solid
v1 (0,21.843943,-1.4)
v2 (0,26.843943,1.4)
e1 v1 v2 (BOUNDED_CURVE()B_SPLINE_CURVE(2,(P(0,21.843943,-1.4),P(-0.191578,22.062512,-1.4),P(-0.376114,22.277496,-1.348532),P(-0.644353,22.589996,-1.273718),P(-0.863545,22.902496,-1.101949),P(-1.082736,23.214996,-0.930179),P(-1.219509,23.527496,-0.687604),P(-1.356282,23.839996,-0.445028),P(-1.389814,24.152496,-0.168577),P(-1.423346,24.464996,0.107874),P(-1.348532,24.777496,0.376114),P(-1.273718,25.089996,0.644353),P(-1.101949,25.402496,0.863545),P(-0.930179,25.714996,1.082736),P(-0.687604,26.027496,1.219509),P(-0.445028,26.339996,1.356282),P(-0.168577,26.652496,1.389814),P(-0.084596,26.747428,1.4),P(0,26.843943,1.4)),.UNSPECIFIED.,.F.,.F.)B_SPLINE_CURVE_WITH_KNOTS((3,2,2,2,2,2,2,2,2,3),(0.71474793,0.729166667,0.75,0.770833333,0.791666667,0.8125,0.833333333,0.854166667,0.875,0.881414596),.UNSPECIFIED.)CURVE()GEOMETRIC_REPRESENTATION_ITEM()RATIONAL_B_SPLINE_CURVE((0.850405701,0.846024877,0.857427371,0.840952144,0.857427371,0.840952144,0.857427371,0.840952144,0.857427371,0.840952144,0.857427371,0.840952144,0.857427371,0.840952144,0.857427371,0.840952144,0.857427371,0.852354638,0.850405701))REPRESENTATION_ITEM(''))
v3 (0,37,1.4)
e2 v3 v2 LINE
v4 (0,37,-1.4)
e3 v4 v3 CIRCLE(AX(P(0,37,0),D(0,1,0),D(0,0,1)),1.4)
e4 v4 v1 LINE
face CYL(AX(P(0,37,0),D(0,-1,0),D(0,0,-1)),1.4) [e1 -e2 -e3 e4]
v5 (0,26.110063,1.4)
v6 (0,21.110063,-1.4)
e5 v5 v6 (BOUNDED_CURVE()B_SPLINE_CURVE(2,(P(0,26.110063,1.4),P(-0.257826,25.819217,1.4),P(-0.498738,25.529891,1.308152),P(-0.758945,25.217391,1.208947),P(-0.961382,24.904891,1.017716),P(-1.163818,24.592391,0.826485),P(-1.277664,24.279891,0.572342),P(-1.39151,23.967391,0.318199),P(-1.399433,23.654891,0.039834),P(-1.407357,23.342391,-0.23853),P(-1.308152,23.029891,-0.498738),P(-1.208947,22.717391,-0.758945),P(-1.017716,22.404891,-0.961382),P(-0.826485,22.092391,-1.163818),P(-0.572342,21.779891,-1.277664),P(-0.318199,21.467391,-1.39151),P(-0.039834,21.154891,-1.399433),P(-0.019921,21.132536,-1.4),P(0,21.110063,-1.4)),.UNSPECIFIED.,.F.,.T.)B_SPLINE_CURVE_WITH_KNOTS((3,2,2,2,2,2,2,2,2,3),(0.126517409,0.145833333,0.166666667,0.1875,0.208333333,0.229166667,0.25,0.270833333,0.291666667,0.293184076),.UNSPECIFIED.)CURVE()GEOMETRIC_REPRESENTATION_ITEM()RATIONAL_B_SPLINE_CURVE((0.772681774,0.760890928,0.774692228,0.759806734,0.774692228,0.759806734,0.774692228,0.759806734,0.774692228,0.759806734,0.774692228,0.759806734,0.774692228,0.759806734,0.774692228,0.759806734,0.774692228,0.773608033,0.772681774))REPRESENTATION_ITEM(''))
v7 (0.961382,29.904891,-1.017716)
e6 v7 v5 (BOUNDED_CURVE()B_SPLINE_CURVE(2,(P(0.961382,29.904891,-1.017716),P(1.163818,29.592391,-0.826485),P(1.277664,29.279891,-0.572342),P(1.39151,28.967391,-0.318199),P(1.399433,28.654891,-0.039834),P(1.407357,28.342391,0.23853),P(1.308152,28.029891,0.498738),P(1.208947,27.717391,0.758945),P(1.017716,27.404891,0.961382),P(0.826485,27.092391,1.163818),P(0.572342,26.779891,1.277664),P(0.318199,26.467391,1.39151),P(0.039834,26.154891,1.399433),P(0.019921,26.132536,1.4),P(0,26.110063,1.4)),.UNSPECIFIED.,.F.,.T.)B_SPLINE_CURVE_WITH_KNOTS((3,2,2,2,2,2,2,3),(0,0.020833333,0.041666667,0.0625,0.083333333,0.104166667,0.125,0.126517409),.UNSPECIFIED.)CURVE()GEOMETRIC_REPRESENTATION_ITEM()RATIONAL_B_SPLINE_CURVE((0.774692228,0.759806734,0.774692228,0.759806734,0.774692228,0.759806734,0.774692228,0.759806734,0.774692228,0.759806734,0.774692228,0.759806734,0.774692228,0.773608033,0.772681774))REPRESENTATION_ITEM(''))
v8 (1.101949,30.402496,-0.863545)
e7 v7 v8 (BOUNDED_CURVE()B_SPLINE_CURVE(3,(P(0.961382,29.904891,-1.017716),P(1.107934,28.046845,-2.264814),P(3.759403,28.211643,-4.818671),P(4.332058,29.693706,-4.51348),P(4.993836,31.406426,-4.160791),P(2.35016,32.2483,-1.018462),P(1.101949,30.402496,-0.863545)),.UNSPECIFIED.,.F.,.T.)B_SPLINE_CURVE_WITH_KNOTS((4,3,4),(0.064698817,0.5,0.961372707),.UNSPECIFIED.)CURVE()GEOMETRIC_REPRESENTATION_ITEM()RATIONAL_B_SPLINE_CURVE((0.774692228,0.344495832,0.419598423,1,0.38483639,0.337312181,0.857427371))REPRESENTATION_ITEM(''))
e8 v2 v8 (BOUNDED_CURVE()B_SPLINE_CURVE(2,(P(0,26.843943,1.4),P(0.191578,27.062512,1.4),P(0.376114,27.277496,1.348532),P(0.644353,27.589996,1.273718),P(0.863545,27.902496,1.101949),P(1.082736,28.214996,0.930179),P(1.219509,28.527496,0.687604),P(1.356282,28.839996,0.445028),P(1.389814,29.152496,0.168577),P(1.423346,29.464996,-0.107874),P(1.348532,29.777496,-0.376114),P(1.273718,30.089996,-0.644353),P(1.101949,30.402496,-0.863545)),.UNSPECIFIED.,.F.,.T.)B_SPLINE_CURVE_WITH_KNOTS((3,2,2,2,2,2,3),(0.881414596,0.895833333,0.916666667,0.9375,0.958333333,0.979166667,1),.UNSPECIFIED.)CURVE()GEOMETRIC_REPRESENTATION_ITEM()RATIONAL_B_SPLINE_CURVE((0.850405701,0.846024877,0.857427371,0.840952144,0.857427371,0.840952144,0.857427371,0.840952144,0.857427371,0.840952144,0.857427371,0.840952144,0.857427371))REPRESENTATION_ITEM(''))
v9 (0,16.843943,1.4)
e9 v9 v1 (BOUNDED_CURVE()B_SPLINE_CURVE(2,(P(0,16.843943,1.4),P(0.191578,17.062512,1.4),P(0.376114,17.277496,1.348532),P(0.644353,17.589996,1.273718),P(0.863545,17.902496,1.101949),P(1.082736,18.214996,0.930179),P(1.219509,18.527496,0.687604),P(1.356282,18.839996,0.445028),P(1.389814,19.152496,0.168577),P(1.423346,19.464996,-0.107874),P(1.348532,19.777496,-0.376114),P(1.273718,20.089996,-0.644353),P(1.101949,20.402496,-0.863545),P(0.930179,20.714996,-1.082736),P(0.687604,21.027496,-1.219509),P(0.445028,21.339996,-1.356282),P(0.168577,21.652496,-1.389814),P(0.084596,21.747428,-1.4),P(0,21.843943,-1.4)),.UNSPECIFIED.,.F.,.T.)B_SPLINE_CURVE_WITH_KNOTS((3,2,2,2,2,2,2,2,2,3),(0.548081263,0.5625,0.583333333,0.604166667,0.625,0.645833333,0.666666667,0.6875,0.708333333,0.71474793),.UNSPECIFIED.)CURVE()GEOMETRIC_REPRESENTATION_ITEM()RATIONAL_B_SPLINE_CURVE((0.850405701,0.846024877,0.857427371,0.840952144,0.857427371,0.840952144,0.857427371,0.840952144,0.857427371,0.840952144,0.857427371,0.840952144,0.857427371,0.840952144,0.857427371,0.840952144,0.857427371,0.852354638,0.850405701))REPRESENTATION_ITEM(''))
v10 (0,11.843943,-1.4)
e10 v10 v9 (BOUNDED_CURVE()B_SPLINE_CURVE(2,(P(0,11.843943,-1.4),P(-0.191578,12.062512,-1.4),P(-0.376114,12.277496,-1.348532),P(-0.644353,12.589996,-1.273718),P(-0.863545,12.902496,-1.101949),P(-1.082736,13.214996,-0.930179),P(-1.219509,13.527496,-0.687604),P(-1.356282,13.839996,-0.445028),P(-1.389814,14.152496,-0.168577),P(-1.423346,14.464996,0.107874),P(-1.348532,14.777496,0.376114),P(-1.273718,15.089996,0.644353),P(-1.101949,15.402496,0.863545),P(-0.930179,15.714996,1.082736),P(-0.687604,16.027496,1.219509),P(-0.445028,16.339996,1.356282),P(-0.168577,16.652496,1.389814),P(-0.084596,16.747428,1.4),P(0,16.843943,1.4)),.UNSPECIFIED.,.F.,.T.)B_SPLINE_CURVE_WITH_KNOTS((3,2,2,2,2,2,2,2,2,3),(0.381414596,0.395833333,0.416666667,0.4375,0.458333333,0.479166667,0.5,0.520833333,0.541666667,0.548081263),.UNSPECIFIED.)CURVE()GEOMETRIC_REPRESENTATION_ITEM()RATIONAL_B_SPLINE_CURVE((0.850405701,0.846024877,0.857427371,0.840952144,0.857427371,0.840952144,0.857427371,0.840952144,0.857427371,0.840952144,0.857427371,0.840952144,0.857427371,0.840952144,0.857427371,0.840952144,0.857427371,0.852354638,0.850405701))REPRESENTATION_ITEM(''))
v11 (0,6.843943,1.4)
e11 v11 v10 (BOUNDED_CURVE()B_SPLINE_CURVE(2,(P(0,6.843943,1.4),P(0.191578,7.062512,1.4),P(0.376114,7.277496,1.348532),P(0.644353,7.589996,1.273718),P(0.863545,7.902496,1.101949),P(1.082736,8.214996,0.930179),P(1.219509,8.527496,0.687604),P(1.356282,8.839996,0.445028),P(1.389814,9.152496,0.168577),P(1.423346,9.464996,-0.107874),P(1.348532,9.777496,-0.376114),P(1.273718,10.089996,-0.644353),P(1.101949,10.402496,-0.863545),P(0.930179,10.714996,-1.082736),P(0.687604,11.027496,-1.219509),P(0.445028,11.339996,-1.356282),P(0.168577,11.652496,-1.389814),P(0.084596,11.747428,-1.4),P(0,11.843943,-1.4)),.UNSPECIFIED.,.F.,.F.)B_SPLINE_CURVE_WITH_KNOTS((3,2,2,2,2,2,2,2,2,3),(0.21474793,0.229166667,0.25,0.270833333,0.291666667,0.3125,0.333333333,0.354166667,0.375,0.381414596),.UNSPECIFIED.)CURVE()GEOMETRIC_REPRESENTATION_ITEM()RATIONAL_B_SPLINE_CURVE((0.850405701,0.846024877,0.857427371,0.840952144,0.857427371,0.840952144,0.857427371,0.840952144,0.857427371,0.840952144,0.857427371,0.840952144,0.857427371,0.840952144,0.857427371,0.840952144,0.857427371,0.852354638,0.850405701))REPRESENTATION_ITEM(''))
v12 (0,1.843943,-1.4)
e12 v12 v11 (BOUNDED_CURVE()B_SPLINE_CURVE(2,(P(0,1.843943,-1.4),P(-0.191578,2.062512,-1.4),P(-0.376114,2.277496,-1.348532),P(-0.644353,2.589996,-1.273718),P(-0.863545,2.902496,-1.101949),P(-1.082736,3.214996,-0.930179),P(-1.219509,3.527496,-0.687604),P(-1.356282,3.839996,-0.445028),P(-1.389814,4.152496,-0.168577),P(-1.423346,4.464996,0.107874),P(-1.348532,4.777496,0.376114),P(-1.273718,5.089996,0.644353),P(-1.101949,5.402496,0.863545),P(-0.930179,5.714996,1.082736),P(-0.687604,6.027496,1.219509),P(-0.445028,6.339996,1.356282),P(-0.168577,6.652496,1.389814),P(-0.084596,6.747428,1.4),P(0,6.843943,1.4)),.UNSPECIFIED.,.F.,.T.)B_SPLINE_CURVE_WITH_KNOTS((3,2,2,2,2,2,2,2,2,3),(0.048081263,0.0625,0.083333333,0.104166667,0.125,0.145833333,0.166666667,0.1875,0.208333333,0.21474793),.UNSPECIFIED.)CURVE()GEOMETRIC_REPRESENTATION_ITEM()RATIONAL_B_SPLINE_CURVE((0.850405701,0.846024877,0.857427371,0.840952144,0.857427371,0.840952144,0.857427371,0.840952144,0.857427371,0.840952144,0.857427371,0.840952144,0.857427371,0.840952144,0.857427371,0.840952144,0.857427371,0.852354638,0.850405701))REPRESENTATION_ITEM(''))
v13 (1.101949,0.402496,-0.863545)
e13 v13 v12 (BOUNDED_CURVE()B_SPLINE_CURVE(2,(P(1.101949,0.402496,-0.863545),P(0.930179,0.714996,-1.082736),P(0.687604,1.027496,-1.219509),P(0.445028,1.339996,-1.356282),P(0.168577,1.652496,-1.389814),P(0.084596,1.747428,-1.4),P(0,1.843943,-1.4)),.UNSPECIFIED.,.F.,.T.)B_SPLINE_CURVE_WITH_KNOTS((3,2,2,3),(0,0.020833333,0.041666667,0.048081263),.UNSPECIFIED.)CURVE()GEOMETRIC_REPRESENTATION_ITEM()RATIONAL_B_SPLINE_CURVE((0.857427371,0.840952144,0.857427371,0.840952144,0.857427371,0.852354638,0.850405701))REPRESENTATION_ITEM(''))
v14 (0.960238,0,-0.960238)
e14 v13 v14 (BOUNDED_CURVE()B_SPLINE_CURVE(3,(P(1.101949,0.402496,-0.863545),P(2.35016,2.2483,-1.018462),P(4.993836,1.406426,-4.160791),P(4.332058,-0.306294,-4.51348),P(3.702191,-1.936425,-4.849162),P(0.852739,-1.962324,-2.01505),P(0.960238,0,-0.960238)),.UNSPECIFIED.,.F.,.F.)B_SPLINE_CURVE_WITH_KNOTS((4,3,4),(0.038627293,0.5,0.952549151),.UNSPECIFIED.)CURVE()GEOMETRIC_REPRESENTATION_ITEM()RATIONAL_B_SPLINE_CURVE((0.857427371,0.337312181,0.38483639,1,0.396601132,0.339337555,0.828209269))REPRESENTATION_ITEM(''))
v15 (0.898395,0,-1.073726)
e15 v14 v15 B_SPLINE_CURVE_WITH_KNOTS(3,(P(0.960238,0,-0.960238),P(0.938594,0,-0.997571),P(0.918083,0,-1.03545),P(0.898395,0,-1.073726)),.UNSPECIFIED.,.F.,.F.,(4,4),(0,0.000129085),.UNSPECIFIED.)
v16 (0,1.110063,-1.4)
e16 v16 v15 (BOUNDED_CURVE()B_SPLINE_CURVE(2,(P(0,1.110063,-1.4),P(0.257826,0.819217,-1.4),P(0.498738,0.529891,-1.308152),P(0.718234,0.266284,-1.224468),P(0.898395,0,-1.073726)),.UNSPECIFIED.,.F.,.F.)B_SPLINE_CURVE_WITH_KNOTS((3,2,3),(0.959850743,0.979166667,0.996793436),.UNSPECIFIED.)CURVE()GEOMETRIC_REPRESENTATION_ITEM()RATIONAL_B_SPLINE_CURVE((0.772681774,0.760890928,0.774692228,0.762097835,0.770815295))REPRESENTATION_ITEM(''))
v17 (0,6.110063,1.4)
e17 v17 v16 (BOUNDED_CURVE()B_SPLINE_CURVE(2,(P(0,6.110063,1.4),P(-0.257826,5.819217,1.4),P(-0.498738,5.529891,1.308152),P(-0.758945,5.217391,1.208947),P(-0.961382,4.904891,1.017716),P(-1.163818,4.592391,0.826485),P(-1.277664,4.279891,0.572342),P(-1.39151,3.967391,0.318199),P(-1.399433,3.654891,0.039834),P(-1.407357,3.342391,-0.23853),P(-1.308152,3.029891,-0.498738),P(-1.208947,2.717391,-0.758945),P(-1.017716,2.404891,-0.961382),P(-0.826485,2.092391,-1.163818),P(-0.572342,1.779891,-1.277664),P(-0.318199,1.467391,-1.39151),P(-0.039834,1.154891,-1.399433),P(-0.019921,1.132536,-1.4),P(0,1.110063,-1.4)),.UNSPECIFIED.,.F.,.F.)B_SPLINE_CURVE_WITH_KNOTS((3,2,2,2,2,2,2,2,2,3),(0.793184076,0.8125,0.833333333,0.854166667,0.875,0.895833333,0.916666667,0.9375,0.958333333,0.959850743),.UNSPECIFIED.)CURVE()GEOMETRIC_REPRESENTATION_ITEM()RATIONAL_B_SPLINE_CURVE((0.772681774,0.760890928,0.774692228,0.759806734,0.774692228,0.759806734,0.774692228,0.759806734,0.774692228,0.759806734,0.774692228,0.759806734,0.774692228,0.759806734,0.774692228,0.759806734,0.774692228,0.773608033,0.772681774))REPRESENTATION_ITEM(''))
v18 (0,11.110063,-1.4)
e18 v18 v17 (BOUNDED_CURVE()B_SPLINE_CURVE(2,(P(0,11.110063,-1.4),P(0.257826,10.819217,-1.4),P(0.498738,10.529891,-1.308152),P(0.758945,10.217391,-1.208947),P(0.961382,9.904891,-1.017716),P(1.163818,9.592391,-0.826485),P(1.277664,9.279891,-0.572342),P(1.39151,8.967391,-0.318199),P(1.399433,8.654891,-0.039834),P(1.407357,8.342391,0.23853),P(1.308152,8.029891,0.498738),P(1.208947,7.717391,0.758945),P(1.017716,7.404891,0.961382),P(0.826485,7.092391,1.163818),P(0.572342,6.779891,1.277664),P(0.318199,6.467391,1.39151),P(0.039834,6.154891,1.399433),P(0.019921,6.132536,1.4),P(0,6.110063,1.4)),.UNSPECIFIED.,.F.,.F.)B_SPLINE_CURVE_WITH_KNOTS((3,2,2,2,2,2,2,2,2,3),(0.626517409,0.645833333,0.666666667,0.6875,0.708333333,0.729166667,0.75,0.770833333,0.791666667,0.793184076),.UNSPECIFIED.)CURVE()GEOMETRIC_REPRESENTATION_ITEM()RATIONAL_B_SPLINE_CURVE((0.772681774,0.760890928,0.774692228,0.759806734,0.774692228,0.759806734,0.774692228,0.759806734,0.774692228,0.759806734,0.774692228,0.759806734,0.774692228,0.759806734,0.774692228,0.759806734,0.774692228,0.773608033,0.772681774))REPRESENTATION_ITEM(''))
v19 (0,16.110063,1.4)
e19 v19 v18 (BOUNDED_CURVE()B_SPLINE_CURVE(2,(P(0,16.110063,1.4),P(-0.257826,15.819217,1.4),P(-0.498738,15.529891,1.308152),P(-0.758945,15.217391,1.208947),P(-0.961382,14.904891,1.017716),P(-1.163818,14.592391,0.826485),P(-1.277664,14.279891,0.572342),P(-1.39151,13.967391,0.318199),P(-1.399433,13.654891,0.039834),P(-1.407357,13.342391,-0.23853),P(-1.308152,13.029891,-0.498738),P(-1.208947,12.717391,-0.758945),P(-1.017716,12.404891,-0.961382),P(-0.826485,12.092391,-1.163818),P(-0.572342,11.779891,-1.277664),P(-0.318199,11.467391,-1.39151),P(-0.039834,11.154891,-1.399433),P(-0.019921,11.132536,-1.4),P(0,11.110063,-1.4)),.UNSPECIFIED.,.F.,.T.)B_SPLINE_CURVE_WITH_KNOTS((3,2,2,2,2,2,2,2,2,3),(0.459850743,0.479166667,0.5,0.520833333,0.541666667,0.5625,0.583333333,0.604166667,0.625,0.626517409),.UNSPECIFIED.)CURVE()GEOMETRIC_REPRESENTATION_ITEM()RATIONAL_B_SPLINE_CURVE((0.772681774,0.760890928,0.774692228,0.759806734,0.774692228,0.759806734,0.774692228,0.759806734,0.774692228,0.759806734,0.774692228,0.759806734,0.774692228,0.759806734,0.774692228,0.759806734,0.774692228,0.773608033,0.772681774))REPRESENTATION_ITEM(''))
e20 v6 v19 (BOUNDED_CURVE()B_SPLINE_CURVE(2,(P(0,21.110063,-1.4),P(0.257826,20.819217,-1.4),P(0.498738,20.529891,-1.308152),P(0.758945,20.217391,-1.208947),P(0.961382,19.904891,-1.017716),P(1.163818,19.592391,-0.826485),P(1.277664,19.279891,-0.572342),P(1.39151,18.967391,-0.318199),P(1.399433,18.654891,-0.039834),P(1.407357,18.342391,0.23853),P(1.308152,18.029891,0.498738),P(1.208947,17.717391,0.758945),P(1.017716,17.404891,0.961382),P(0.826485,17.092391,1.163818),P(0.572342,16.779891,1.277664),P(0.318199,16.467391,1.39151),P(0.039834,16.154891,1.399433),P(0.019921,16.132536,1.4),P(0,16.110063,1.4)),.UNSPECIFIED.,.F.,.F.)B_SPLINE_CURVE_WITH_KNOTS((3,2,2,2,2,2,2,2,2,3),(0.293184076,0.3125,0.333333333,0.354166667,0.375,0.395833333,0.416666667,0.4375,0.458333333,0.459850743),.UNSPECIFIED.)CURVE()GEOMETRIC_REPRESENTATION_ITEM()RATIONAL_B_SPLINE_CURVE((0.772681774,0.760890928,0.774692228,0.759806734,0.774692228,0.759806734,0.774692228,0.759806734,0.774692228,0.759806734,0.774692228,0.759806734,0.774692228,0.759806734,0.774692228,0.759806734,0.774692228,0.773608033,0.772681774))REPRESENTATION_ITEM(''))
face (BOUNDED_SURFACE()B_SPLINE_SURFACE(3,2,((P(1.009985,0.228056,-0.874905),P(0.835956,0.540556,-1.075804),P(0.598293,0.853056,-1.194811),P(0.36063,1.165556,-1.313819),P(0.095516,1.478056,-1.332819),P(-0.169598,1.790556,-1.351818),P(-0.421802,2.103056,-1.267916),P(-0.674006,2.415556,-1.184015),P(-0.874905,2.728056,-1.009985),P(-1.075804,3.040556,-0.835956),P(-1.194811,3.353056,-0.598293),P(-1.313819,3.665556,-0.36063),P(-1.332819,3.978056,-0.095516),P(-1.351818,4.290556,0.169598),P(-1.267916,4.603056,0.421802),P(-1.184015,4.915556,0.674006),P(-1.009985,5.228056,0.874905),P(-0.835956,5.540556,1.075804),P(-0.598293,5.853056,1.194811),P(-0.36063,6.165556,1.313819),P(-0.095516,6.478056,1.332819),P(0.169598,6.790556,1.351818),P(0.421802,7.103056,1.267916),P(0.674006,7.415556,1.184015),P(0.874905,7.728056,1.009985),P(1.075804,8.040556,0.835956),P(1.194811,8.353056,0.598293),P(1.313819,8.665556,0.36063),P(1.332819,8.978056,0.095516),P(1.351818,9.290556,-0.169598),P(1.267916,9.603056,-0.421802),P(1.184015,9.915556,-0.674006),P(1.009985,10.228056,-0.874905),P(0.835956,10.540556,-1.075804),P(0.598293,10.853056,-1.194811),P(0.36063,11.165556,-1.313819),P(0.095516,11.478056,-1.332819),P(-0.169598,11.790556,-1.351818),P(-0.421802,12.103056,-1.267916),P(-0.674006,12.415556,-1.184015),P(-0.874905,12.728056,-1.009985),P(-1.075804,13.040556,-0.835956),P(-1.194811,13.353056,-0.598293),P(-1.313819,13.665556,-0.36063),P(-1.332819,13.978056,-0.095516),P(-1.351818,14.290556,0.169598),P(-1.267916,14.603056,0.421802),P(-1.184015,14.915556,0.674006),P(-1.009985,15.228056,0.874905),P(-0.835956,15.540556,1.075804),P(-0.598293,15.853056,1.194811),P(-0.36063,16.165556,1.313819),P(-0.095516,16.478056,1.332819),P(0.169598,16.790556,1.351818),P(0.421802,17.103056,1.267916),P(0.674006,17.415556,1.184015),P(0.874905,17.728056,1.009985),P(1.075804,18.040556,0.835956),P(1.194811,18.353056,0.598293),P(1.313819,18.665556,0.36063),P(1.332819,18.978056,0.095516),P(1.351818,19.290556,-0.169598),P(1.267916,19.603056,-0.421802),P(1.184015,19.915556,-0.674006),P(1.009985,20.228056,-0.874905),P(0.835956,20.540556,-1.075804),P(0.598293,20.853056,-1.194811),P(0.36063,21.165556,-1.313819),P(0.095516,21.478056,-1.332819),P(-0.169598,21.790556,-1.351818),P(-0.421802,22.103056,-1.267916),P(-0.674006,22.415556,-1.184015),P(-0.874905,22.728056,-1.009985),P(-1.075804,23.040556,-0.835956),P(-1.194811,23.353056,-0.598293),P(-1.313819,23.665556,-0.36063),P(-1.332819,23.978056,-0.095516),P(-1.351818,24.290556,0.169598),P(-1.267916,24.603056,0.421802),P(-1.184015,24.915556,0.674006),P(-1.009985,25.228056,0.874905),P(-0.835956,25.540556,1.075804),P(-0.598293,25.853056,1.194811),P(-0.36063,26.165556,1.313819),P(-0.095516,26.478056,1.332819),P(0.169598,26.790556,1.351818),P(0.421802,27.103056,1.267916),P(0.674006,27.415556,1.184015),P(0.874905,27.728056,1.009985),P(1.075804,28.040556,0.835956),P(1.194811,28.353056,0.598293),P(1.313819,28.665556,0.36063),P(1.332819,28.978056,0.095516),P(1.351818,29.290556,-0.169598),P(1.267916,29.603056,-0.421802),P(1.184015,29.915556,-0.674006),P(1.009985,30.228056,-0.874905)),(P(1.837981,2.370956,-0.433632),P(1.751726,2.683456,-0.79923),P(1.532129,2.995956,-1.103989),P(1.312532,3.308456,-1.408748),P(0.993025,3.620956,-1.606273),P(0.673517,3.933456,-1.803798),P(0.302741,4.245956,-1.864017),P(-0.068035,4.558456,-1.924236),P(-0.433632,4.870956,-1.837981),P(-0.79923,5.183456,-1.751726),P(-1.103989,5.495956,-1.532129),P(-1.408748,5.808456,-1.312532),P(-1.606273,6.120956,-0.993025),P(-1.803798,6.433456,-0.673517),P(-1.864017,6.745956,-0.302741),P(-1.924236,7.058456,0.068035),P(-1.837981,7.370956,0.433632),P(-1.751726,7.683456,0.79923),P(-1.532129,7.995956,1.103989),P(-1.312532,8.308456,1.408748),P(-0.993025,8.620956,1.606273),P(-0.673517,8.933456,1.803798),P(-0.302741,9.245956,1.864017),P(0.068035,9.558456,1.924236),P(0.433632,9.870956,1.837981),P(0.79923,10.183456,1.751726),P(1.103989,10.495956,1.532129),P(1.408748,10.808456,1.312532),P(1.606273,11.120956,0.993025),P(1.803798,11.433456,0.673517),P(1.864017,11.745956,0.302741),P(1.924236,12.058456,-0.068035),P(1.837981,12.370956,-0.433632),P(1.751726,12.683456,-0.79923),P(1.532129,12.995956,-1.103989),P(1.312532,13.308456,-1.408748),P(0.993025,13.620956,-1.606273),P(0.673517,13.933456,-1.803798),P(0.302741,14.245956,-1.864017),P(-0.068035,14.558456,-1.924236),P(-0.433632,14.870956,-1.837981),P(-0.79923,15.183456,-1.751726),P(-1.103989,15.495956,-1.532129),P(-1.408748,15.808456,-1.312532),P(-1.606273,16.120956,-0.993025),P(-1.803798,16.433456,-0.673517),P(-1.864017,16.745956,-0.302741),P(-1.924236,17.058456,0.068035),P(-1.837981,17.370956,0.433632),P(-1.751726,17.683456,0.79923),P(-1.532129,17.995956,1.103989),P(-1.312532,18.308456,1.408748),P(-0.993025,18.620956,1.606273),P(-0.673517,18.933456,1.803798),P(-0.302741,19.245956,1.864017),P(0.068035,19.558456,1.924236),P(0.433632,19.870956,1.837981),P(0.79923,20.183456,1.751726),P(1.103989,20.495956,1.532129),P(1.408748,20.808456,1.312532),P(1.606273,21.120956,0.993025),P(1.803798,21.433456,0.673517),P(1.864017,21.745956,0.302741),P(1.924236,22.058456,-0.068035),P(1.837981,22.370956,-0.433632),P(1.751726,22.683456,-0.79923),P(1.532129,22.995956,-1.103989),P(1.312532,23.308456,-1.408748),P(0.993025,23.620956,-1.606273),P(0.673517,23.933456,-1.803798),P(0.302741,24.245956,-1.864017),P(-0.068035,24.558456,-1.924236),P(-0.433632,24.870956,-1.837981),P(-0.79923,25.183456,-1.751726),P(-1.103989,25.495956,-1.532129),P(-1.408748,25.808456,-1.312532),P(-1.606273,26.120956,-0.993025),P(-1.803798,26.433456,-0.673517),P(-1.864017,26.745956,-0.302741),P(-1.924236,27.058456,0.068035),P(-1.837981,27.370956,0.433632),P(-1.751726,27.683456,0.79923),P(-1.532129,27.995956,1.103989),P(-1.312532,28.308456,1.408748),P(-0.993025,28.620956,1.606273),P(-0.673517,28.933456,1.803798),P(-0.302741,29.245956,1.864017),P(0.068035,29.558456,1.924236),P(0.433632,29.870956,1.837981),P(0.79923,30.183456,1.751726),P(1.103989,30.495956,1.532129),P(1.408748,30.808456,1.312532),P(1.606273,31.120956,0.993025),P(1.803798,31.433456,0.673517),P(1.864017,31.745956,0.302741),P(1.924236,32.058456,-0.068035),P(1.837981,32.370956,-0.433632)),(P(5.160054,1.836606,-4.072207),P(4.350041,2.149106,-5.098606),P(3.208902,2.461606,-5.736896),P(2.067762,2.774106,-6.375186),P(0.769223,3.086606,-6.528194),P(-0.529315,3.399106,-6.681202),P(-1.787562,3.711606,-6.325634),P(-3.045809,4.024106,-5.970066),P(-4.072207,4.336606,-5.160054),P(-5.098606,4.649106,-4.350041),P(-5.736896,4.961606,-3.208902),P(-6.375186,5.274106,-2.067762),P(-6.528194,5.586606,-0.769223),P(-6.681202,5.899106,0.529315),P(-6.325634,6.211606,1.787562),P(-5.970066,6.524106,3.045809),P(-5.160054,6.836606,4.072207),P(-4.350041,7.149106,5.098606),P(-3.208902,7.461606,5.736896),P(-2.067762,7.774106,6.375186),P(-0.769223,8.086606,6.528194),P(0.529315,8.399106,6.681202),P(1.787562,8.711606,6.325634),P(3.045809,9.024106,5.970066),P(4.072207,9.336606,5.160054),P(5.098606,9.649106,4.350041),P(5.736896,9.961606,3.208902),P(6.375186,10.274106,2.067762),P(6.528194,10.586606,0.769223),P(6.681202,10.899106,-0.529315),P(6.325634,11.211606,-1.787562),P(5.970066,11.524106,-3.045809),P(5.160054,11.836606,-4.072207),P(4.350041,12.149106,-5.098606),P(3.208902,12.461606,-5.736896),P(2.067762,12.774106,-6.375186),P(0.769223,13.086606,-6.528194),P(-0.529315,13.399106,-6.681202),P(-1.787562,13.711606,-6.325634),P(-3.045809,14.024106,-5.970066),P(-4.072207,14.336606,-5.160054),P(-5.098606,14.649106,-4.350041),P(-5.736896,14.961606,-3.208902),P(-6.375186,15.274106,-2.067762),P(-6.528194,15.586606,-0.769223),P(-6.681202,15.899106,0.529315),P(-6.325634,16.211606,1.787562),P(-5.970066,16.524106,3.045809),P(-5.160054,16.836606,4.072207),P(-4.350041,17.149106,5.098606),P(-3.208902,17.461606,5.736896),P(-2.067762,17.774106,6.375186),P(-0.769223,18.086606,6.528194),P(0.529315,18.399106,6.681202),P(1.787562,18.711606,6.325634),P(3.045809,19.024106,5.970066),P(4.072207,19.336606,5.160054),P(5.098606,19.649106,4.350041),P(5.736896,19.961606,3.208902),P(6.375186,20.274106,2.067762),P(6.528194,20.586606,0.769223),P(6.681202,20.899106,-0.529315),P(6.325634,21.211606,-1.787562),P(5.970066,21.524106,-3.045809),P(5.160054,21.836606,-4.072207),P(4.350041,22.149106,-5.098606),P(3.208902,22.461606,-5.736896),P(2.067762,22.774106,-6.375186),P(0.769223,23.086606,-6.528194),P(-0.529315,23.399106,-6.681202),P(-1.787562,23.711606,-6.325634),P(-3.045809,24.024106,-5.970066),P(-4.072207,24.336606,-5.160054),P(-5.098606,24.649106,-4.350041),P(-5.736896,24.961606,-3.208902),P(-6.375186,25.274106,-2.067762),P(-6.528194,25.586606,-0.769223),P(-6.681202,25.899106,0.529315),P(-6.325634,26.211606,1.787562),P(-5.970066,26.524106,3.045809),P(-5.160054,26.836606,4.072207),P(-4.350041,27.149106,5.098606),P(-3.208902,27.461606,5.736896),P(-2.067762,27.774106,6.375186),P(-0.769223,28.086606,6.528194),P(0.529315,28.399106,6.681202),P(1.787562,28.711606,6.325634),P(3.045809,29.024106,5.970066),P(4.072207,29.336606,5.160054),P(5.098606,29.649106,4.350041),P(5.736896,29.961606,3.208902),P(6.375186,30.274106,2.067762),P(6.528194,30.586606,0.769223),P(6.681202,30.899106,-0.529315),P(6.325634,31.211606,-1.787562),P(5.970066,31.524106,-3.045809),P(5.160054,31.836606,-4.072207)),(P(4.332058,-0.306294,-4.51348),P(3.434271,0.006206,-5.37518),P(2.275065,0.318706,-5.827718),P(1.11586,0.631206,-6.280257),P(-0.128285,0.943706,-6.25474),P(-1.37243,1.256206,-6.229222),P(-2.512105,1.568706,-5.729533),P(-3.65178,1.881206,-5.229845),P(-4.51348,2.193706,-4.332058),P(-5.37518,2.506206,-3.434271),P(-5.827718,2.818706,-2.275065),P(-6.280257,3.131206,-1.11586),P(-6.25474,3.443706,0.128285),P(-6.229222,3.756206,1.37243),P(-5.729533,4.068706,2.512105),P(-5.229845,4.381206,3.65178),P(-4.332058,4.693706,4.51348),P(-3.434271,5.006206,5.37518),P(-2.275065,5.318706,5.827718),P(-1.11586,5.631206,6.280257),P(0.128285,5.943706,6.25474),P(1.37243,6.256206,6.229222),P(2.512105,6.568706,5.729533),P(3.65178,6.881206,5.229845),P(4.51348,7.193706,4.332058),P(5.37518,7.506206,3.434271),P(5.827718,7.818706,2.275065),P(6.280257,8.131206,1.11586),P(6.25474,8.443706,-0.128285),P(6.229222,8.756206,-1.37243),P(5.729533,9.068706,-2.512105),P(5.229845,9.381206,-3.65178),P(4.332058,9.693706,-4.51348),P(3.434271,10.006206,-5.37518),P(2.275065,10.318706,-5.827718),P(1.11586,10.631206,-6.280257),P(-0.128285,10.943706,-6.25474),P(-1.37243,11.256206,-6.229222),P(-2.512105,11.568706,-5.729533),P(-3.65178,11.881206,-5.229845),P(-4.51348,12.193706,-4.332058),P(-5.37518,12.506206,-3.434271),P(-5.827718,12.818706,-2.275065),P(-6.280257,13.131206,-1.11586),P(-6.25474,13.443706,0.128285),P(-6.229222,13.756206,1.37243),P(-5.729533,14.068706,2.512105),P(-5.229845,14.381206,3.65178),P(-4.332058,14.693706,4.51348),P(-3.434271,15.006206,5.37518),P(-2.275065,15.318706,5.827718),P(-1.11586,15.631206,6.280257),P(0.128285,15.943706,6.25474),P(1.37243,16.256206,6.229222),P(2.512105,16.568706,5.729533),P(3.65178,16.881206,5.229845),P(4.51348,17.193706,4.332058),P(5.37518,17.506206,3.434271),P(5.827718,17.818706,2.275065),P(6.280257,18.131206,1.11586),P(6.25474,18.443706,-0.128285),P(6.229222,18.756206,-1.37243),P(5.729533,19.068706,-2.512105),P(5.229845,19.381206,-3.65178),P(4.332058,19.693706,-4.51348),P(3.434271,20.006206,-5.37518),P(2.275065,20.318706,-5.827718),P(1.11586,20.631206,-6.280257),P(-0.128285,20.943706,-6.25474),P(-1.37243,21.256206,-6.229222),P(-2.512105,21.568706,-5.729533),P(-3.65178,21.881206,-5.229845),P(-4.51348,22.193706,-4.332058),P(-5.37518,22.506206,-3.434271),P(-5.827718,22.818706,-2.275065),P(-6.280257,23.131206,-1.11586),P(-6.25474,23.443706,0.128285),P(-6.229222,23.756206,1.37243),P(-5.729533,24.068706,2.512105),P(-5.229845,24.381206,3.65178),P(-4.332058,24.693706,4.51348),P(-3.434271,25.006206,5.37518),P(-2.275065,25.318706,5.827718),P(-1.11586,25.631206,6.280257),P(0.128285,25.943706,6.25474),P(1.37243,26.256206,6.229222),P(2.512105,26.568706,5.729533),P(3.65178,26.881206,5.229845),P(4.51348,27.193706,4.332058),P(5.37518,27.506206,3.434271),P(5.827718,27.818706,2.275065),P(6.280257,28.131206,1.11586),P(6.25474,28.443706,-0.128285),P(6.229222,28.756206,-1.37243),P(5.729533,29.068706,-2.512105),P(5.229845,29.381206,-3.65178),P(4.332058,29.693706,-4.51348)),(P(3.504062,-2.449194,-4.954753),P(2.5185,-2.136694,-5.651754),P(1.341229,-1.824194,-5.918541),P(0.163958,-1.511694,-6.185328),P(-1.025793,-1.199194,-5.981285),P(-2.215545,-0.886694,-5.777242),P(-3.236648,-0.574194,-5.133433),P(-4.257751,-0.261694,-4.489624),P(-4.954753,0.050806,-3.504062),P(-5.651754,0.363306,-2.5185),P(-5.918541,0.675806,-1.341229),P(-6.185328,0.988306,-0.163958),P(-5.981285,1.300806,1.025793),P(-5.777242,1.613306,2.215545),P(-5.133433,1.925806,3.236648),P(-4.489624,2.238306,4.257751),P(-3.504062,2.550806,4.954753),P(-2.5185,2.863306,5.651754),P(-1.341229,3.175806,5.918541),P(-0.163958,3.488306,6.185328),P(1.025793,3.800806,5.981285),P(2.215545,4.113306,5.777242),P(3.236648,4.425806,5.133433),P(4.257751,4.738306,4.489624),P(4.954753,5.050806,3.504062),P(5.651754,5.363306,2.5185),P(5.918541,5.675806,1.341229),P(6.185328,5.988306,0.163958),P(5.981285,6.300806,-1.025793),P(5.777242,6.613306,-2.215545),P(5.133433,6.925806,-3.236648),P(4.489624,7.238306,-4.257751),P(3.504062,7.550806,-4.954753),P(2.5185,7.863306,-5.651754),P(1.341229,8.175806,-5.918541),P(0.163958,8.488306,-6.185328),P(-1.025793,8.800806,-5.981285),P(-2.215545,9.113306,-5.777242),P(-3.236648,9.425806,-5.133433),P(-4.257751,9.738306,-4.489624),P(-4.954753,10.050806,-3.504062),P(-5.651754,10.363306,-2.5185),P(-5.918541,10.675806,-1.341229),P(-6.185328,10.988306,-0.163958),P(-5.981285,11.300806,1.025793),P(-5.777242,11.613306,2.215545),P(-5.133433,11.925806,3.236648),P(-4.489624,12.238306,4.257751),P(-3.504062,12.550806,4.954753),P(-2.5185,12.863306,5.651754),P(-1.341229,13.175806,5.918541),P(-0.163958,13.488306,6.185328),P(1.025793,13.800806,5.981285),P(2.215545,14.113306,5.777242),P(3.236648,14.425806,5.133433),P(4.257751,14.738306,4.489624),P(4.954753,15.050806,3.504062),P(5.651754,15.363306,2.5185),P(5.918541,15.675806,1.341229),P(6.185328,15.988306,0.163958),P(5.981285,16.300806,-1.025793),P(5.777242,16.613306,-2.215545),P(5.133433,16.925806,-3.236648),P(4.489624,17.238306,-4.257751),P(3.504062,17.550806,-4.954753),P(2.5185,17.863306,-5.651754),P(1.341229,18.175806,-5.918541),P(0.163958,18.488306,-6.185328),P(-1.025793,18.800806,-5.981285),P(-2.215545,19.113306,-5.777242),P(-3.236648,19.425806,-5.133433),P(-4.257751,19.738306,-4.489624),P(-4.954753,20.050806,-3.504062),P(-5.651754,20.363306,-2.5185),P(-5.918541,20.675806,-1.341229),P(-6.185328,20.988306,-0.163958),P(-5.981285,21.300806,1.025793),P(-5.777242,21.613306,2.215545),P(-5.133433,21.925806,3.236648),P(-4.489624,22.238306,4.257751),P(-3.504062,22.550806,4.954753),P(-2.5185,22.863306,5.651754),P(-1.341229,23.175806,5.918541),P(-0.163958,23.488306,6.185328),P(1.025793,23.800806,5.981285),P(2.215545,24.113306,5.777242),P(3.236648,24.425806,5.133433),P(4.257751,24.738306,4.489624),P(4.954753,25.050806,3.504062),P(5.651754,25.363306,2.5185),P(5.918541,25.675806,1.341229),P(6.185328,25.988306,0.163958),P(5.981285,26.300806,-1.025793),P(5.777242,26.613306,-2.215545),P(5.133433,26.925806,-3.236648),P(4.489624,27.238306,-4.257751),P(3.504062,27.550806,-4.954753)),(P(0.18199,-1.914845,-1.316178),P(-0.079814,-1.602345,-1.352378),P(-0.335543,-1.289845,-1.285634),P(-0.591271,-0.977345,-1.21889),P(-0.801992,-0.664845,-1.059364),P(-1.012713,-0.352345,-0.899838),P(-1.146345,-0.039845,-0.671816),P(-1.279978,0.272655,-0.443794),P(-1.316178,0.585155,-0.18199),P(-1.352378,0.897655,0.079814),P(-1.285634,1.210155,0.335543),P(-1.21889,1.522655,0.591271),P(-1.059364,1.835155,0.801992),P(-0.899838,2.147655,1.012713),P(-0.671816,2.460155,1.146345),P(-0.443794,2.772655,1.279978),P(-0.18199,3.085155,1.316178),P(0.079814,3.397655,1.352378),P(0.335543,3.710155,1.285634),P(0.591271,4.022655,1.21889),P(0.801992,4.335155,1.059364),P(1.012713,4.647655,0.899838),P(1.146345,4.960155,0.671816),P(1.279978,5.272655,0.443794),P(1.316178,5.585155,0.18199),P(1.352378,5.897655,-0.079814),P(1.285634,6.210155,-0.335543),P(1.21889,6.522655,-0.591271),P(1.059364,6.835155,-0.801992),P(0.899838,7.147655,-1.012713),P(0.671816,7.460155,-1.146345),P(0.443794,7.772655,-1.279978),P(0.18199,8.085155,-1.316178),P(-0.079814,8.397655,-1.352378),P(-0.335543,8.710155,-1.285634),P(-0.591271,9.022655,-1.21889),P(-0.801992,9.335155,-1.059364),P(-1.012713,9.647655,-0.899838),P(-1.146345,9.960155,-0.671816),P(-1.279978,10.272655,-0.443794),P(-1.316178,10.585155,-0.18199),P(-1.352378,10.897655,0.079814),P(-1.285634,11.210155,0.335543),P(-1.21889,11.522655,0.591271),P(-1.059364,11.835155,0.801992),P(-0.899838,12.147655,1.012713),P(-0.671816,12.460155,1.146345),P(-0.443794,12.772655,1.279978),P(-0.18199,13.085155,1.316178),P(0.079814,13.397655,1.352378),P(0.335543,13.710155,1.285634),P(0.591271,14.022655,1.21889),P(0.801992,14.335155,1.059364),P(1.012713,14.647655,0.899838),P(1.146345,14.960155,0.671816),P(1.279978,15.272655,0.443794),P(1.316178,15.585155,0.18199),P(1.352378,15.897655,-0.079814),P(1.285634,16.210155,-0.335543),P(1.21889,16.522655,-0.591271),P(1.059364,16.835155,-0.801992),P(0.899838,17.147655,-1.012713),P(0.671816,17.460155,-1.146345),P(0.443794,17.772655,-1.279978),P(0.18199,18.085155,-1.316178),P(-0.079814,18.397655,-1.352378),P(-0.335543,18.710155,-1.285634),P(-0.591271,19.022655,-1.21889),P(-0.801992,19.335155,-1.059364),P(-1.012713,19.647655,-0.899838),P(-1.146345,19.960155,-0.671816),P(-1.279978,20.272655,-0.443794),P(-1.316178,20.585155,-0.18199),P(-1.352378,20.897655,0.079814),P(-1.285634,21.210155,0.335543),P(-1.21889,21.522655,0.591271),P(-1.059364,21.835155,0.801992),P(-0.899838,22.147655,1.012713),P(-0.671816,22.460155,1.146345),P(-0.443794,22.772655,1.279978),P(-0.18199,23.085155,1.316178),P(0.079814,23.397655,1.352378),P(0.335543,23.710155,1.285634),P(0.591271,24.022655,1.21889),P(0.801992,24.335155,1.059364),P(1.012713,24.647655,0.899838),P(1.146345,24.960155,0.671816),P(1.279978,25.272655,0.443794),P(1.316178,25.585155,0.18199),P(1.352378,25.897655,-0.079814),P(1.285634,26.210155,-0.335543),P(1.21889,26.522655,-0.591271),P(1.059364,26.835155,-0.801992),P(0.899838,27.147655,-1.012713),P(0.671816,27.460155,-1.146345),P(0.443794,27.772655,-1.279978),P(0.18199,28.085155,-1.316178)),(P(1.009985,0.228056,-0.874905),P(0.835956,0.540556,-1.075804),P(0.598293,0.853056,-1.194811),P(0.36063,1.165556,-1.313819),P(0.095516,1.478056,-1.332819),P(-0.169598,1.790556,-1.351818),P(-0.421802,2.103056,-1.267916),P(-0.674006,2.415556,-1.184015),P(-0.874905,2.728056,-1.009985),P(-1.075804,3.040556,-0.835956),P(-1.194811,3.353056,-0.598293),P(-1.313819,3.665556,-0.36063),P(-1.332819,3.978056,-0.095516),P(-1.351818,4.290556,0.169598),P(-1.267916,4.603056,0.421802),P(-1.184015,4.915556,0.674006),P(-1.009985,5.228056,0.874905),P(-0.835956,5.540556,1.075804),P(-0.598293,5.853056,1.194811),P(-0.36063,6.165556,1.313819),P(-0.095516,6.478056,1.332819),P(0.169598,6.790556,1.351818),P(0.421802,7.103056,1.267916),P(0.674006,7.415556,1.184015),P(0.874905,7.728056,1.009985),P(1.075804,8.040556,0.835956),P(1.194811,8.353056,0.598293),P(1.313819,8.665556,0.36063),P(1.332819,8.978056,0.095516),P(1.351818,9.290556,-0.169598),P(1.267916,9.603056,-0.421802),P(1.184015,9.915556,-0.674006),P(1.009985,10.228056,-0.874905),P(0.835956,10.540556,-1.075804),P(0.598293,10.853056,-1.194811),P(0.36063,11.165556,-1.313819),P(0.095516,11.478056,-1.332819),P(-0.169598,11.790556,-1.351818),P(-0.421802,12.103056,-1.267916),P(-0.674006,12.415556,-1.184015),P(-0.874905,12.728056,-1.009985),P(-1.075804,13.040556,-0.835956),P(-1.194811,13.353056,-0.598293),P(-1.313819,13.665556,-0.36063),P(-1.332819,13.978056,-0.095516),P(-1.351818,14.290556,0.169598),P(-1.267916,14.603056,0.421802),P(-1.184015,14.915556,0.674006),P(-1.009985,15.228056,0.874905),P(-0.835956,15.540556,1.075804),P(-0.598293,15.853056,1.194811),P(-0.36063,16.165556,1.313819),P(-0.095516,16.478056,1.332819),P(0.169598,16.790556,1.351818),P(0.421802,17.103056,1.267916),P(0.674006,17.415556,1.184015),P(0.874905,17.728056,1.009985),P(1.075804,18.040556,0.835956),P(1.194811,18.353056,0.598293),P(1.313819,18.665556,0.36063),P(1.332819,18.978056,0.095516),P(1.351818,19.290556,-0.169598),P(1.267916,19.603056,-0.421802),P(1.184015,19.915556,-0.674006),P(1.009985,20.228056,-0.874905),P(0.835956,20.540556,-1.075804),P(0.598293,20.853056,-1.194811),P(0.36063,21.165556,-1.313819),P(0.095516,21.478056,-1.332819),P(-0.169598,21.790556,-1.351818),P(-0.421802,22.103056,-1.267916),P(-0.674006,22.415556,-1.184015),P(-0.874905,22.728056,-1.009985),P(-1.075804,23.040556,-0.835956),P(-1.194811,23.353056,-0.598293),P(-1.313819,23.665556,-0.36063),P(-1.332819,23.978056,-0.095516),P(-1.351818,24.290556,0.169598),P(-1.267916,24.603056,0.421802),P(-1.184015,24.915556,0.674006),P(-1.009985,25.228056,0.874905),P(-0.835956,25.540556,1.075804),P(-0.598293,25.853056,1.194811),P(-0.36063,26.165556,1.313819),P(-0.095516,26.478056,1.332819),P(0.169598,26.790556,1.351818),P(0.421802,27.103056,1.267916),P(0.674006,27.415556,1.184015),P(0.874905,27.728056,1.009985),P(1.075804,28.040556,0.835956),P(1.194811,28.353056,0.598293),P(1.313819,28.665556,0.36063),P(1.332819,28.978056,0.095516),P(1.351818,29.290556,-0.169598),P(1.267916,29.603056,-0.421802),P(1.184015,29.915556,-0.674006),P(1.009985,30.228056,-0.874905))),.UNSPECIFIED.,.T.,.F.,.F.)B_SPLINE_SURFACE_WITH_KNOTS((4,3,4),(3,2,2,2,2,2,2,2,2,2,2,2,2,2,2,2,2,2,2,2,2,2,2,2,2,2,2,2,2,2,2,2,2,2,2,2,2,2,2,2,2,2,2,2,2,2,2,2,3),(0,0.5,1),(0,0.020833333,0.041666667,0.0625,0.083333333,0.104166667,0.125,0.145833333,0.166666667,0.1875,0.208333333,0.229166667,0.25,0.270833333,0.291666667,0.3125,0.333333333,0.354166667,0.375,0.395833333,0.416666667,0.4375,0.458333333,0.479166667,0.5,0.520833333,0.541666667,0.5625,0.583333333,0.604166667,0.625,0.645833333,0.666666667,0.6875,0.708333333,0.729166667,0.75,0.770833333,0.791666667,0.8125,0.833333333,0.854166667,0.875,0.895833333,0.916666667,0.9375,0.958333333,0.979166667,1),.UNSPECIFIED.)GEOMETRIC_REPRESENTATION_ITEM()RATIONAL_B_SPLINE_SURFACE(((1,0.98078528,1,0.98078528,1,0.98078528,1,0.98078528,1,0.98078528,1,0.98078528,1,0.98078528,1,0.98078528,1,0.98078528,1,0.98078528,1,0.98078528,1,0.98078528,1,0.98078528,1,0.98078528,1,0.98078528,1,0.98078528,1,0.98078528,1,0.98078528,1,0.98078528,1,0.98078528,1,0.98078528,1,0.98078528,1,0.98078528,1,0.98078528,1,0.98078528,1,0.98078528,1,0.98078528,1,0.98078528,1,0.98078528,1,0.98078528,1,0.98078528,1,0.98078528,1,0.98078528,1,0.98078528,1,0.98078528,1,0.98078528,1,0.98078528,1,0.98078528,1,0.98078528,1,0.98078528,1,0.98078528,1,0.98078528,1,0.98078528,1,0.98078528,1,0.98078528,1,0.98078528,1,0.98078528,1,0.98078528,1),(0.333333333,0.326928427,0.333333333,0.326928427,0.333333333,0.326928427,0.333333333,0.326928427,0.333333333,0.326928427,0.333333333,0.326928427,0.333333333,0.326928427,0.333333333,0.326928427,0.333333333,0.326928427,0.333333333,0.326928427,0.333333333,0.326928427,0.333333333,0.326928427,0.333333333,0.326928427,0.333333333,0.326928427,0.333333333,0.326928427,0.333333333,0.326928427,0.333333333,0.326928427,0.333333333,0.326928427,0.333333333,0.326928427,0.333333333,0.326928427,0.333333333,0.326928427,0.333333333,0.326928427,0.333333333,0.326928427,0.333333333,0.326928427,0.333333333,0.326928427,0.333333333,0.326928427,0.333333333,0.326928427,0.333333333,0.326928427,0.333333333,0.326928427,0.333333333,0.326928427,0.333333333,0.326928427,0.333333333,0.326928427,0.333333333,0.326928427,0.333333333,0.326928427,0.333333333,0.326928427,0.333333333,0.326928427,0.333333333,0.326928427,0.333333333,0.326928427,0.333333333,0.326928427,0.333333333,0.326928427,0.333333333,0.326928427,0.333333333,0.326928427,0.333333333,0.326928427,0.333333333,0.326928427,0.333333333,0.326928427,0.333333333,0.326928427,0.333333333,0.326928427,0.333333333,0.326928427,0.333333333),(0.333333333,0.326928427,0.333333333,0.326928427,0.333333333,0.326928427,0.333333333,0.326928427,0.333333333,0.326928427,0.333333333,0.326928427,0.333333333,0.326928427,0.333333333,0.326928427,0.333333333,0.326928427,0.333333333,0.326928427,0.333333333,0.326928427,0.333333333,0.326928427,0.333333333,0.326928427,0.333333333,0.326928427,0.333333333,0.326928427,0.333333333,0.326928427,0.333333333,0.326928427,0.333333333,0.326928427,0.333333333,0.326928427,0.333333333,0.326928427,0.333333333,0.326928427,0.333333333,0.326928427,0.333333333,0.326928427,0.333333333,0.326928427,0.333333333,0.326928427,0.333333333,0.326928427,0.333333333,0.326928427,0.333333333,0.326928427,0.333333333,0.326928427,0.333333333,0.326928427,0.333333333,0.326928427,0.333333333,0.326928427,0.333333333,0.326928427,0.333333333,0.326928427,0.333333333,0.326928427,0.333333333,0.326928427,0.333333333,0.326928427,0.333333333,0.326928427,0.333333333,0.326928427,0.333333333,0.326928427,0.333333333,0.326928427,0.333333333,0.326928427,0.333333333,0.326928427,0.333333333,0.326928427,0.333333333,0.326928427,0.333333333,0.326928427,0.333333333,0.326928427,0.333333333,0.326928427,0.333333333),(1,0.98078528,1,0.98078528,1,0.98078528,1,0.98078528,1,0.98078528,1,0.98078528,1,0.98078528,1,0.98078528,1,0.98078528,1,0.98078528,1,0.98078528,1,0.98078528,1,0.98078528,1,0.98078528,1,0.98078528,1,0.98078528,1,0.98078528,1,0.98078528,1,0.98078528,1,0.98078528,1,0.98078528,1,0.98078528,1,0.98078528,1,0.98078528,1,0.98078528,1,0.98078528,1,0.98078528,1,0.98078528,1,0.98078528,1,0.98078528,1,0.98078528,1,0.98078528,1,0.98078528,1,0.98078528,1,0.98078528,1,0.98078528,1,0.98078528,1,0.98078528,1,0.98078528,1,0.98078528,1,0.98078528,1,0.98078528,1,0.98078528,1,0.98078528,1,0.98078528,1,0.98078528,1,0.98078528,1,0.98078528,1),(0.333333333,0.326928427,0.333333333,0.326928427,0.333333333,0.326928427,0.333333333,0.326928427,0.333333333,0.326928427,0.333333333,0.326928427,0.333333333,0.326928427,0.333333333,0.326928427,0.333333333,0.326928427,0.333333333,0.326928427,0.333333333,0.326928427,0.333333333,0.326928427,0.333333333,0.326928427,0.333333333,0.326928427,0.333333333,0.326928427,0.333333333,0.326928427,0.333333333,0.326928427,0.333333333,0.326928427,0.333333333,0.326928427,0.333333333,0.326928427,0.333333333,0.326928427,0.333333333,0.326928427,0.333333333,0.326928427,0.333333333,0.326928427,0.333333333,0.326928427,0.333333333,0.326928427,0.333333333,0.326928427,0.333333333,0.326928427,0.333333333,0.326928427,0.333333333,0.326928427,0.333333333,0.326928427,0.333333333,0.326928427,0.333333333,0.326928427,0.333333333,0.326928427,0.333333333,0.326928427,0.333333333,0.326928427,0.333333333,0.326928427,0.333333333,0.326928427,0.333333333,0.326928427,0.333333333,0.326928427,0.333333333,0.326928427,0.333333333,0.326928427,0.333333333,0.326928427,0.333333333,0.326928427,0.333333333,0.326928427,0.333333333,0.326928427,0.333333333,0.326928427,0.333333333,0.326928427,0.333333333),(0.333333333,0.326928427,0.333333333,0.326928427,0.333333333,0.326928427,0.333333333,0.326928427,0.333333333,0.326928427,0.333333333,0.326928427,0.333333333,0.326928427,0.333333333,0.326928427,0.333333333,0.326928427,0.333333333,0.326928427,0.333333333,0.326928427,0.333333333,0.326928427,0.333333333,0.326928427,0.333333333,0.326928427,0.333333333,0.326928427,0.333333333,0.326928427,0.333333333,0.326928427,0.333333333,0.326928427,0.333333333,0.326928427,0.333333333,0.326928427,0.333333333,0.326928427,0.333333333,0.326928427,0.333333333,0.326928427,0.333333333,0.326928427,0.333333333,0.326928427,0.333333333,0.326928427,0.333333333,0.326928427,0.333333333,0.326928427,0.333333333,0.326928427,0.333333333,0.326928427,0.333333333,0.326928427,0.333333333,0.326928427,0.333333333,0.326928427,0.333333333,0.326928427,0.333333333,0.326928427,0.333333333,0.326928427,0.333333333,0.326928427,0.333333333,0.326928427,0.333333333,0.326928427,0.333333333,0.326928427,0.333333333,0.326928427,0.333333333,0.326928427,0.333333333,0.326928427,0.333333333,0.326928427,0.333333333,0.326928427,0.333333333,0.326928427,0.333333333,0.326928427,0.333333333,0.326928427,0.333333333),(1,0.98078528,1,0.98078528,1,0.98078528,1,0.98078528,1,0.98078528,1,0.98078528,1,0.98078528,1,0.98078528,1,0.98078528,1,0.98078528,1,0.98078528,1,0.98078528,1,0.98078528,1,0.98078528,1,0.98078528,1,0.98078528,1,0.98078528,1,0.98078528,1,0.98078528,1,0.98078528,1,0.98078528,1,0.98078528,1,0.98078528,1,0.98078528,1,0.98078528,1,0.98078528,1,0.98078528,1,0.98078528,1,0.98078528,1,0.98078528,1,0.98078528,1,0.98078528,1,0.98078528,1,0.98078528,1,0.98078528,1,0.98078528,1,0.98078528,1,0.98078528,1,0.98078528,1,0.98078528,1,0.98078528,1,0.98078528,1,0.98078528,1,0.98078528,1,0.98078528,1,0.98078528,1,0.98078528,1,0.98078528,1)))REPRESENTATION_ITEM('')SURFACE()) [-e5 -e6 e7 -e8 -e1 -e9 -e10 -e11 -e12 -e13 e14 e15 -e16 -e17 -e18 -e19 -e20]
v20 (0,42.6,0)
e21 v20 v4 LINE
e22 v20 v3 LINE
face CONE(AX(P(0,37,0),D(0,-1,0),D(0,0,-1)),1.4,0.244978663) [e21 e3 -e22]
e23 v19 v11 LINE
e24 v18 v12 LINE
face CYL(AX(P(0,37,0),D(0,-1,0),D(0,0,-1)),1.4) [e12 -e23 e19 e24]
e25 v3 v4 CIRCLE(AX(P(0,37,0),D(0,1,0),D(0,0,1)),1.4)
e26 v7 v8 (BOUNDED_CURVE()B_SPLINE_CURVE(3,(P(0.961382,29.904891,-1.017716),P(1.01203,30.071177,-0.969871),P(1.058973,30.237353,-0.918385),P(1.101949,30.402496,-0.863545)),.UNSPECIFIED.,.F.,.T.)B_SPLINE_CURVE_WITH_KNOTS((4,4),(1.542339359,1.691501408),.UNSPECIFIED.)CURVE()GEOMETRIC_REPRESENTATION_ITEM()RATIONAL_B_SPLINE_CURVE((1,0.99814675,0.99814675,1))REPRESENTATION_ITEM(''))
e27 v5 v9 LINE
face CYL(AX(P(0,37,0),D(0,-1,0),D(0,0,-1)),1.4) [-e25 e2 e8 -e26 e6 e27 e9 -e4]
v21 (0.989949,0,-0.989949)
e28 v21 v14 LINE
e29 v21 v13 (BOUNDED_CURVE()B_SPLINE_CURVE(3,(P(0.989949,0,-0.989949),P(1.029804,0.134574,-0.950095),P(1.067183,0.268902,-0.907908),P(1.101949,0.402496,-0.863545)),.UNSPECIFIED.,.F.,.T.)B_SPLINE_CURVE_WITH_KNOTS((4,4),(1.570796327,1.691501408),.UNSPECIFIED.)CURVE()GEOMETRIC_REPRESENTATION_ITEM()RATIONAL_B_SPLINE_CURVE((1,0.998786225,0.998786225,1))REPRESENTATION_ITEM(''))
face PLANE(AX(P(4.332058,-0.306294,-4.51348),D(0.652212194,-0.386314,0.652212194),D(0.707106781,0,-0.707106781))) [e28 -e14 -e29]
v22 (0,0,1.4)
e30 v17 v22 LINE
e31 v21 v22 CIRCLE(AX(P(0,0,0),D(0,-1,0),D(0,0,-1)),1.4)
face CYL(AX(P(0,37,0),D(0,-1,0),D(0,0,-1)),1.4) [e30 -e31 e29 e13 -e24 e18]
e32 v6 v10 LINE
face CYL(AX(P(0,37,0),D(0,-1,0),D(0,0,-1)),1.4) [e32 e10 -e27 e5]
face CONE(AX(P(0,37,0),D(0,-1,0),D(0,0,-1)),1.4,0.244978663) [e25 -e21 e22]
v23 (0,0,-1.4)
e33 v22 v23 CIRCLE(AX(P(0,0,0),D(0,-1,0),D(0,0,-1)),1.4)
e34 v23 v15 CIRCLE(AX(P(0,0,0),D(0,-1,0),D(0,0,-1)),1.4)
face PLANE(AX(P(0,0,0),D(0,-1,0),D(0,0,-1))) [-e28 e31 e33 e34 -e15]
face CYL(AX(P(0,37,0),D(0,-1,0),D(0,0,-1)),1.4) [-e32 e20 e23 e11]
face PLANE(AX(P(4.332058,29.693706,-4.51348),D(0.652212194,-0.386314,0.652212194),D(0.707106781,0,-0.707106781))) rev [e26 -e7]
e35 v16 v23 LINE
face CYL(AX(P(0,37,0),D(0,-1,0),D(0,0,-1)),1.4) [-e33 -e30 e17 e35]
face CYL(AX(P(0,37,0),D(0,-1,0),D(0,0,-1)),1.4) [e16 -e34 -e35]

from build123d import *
from build123d.topology import SkipClean

# Parameters (mm, degrees)
SHAFT_SKETCH_R             = 1.4
SHAFT_37MM_DEPTH           = 37
SHAFT_END_CUT_SKETCH_R     = 1.4
SHAFT_END_CUT_10MM_DEPTH   = 10
SHAFT_START                = 10
SHAFT_EXTENSION_SKETCH_R   = 1.4
SHAFT_EXTENSION_10MM_DEPTH = 10
COIL_WIRE_PITCH            = 10
COIL_WIRE_HEIGHT           = 30
COIL_WIRE_RADIUS           = 3.8
COIL_WIRE_START_ANGLE      = 135
COIL_WIRE_PROFILE_RX       = 2.477948864
COIL_WIRE_PROFILE_RY       = 1.169649495


with BuildPart() as part:
    # Shaft Sketch → Shaft 37mm (new body)
    with BuildSketch(Plane(origin=(0, 0, 0), x_dir=(1, 0, 0), z_dir=(0, 1, 0))):
        with Locations(Location((0, 0, 0), (0, 0, 270))):
            Circle(SHAFT_SKETCH_R)
    extrude(amount=SHAFT_37MM_DEPTH)

    # Tip Cone Profile → Conical Tip (revolve)
    with BuildSketch(Plane.XY, mode=Mode.PRIVATE) as conical_tip_sk:
        Polygon((0, 37), (0, 42.6), (1.4, 37), align=None)
    revolve(conical_tip_sk.sketch.rotate(Axis((0, 37, 0), (0, 1, 0)), 90), axis=Axis((0, 37, 0), (0, 1, 0)))

    # Shaft End Cut Sketch → Shaft End Cut 10mm (cut)
    with BuildSketch(Plane.XZ):
        with Locations(Location((0, 0, 0), (0, 0, 270))):
            Circle(SHAFT_END_CUT_SKETCH_R)
    extrude(amount=-SHAFT_END_CUT_10MM_DEPTH, mode=Mode.SUBTRACT)

    # Shaft Extension Sketch → Shaft Extension 10mm (add)
    with BuildSketch(Plane.XZ.offset(-10).offset(SHAFT_START)):
        with Locations(Location((0, 0, 0), (0, 0, 270))):
            Circle(SHAFT_EXTENSION_SKETCH_R)
    extrude(amount=-SHAFT_EXTENSION_10MM_DEPTH)

    # Coil Wire: sweep along a helix
    with SkipClean():  # the faces are left unmerged after this step: merging them gives an invalid solid
        with BuildLine() as coil_wire_path:
            add(Helix(COIL_WIRE_PITCH, COIL_WIRE_HEIGHT, COIL_WIRE_RADIUS, center=(0, 0, 0), direction=(0, 1, 0), mode=Mode.PRIVATE).rotate(Axis((0, 0, 0), (0, 1, 0)), COIL_WIRE_START_ANGLE))
        # Coil Wire Profile → Coil Wire (sweep)
        with BuildSketch(Plane(origin=(2.687005769, 30, -2.687005769), x_dir=(-0.5611613384925322, 0.3323833612114232, 0.758036445938496), z_dir=(-0.652212194480449, 0.3863140001890473, -0.6522121944803959))):
            with Locations(Location((-0.009480676, -0.041804133), (0, 0, -14.409252287))):
                Ellipse(COIL_WIRE_PROFILE_RX, COIL_WIRE_PROFILE_RY)
        sweep(path=coil_wire_path.line, is_frenet=True)


solid = part.part
